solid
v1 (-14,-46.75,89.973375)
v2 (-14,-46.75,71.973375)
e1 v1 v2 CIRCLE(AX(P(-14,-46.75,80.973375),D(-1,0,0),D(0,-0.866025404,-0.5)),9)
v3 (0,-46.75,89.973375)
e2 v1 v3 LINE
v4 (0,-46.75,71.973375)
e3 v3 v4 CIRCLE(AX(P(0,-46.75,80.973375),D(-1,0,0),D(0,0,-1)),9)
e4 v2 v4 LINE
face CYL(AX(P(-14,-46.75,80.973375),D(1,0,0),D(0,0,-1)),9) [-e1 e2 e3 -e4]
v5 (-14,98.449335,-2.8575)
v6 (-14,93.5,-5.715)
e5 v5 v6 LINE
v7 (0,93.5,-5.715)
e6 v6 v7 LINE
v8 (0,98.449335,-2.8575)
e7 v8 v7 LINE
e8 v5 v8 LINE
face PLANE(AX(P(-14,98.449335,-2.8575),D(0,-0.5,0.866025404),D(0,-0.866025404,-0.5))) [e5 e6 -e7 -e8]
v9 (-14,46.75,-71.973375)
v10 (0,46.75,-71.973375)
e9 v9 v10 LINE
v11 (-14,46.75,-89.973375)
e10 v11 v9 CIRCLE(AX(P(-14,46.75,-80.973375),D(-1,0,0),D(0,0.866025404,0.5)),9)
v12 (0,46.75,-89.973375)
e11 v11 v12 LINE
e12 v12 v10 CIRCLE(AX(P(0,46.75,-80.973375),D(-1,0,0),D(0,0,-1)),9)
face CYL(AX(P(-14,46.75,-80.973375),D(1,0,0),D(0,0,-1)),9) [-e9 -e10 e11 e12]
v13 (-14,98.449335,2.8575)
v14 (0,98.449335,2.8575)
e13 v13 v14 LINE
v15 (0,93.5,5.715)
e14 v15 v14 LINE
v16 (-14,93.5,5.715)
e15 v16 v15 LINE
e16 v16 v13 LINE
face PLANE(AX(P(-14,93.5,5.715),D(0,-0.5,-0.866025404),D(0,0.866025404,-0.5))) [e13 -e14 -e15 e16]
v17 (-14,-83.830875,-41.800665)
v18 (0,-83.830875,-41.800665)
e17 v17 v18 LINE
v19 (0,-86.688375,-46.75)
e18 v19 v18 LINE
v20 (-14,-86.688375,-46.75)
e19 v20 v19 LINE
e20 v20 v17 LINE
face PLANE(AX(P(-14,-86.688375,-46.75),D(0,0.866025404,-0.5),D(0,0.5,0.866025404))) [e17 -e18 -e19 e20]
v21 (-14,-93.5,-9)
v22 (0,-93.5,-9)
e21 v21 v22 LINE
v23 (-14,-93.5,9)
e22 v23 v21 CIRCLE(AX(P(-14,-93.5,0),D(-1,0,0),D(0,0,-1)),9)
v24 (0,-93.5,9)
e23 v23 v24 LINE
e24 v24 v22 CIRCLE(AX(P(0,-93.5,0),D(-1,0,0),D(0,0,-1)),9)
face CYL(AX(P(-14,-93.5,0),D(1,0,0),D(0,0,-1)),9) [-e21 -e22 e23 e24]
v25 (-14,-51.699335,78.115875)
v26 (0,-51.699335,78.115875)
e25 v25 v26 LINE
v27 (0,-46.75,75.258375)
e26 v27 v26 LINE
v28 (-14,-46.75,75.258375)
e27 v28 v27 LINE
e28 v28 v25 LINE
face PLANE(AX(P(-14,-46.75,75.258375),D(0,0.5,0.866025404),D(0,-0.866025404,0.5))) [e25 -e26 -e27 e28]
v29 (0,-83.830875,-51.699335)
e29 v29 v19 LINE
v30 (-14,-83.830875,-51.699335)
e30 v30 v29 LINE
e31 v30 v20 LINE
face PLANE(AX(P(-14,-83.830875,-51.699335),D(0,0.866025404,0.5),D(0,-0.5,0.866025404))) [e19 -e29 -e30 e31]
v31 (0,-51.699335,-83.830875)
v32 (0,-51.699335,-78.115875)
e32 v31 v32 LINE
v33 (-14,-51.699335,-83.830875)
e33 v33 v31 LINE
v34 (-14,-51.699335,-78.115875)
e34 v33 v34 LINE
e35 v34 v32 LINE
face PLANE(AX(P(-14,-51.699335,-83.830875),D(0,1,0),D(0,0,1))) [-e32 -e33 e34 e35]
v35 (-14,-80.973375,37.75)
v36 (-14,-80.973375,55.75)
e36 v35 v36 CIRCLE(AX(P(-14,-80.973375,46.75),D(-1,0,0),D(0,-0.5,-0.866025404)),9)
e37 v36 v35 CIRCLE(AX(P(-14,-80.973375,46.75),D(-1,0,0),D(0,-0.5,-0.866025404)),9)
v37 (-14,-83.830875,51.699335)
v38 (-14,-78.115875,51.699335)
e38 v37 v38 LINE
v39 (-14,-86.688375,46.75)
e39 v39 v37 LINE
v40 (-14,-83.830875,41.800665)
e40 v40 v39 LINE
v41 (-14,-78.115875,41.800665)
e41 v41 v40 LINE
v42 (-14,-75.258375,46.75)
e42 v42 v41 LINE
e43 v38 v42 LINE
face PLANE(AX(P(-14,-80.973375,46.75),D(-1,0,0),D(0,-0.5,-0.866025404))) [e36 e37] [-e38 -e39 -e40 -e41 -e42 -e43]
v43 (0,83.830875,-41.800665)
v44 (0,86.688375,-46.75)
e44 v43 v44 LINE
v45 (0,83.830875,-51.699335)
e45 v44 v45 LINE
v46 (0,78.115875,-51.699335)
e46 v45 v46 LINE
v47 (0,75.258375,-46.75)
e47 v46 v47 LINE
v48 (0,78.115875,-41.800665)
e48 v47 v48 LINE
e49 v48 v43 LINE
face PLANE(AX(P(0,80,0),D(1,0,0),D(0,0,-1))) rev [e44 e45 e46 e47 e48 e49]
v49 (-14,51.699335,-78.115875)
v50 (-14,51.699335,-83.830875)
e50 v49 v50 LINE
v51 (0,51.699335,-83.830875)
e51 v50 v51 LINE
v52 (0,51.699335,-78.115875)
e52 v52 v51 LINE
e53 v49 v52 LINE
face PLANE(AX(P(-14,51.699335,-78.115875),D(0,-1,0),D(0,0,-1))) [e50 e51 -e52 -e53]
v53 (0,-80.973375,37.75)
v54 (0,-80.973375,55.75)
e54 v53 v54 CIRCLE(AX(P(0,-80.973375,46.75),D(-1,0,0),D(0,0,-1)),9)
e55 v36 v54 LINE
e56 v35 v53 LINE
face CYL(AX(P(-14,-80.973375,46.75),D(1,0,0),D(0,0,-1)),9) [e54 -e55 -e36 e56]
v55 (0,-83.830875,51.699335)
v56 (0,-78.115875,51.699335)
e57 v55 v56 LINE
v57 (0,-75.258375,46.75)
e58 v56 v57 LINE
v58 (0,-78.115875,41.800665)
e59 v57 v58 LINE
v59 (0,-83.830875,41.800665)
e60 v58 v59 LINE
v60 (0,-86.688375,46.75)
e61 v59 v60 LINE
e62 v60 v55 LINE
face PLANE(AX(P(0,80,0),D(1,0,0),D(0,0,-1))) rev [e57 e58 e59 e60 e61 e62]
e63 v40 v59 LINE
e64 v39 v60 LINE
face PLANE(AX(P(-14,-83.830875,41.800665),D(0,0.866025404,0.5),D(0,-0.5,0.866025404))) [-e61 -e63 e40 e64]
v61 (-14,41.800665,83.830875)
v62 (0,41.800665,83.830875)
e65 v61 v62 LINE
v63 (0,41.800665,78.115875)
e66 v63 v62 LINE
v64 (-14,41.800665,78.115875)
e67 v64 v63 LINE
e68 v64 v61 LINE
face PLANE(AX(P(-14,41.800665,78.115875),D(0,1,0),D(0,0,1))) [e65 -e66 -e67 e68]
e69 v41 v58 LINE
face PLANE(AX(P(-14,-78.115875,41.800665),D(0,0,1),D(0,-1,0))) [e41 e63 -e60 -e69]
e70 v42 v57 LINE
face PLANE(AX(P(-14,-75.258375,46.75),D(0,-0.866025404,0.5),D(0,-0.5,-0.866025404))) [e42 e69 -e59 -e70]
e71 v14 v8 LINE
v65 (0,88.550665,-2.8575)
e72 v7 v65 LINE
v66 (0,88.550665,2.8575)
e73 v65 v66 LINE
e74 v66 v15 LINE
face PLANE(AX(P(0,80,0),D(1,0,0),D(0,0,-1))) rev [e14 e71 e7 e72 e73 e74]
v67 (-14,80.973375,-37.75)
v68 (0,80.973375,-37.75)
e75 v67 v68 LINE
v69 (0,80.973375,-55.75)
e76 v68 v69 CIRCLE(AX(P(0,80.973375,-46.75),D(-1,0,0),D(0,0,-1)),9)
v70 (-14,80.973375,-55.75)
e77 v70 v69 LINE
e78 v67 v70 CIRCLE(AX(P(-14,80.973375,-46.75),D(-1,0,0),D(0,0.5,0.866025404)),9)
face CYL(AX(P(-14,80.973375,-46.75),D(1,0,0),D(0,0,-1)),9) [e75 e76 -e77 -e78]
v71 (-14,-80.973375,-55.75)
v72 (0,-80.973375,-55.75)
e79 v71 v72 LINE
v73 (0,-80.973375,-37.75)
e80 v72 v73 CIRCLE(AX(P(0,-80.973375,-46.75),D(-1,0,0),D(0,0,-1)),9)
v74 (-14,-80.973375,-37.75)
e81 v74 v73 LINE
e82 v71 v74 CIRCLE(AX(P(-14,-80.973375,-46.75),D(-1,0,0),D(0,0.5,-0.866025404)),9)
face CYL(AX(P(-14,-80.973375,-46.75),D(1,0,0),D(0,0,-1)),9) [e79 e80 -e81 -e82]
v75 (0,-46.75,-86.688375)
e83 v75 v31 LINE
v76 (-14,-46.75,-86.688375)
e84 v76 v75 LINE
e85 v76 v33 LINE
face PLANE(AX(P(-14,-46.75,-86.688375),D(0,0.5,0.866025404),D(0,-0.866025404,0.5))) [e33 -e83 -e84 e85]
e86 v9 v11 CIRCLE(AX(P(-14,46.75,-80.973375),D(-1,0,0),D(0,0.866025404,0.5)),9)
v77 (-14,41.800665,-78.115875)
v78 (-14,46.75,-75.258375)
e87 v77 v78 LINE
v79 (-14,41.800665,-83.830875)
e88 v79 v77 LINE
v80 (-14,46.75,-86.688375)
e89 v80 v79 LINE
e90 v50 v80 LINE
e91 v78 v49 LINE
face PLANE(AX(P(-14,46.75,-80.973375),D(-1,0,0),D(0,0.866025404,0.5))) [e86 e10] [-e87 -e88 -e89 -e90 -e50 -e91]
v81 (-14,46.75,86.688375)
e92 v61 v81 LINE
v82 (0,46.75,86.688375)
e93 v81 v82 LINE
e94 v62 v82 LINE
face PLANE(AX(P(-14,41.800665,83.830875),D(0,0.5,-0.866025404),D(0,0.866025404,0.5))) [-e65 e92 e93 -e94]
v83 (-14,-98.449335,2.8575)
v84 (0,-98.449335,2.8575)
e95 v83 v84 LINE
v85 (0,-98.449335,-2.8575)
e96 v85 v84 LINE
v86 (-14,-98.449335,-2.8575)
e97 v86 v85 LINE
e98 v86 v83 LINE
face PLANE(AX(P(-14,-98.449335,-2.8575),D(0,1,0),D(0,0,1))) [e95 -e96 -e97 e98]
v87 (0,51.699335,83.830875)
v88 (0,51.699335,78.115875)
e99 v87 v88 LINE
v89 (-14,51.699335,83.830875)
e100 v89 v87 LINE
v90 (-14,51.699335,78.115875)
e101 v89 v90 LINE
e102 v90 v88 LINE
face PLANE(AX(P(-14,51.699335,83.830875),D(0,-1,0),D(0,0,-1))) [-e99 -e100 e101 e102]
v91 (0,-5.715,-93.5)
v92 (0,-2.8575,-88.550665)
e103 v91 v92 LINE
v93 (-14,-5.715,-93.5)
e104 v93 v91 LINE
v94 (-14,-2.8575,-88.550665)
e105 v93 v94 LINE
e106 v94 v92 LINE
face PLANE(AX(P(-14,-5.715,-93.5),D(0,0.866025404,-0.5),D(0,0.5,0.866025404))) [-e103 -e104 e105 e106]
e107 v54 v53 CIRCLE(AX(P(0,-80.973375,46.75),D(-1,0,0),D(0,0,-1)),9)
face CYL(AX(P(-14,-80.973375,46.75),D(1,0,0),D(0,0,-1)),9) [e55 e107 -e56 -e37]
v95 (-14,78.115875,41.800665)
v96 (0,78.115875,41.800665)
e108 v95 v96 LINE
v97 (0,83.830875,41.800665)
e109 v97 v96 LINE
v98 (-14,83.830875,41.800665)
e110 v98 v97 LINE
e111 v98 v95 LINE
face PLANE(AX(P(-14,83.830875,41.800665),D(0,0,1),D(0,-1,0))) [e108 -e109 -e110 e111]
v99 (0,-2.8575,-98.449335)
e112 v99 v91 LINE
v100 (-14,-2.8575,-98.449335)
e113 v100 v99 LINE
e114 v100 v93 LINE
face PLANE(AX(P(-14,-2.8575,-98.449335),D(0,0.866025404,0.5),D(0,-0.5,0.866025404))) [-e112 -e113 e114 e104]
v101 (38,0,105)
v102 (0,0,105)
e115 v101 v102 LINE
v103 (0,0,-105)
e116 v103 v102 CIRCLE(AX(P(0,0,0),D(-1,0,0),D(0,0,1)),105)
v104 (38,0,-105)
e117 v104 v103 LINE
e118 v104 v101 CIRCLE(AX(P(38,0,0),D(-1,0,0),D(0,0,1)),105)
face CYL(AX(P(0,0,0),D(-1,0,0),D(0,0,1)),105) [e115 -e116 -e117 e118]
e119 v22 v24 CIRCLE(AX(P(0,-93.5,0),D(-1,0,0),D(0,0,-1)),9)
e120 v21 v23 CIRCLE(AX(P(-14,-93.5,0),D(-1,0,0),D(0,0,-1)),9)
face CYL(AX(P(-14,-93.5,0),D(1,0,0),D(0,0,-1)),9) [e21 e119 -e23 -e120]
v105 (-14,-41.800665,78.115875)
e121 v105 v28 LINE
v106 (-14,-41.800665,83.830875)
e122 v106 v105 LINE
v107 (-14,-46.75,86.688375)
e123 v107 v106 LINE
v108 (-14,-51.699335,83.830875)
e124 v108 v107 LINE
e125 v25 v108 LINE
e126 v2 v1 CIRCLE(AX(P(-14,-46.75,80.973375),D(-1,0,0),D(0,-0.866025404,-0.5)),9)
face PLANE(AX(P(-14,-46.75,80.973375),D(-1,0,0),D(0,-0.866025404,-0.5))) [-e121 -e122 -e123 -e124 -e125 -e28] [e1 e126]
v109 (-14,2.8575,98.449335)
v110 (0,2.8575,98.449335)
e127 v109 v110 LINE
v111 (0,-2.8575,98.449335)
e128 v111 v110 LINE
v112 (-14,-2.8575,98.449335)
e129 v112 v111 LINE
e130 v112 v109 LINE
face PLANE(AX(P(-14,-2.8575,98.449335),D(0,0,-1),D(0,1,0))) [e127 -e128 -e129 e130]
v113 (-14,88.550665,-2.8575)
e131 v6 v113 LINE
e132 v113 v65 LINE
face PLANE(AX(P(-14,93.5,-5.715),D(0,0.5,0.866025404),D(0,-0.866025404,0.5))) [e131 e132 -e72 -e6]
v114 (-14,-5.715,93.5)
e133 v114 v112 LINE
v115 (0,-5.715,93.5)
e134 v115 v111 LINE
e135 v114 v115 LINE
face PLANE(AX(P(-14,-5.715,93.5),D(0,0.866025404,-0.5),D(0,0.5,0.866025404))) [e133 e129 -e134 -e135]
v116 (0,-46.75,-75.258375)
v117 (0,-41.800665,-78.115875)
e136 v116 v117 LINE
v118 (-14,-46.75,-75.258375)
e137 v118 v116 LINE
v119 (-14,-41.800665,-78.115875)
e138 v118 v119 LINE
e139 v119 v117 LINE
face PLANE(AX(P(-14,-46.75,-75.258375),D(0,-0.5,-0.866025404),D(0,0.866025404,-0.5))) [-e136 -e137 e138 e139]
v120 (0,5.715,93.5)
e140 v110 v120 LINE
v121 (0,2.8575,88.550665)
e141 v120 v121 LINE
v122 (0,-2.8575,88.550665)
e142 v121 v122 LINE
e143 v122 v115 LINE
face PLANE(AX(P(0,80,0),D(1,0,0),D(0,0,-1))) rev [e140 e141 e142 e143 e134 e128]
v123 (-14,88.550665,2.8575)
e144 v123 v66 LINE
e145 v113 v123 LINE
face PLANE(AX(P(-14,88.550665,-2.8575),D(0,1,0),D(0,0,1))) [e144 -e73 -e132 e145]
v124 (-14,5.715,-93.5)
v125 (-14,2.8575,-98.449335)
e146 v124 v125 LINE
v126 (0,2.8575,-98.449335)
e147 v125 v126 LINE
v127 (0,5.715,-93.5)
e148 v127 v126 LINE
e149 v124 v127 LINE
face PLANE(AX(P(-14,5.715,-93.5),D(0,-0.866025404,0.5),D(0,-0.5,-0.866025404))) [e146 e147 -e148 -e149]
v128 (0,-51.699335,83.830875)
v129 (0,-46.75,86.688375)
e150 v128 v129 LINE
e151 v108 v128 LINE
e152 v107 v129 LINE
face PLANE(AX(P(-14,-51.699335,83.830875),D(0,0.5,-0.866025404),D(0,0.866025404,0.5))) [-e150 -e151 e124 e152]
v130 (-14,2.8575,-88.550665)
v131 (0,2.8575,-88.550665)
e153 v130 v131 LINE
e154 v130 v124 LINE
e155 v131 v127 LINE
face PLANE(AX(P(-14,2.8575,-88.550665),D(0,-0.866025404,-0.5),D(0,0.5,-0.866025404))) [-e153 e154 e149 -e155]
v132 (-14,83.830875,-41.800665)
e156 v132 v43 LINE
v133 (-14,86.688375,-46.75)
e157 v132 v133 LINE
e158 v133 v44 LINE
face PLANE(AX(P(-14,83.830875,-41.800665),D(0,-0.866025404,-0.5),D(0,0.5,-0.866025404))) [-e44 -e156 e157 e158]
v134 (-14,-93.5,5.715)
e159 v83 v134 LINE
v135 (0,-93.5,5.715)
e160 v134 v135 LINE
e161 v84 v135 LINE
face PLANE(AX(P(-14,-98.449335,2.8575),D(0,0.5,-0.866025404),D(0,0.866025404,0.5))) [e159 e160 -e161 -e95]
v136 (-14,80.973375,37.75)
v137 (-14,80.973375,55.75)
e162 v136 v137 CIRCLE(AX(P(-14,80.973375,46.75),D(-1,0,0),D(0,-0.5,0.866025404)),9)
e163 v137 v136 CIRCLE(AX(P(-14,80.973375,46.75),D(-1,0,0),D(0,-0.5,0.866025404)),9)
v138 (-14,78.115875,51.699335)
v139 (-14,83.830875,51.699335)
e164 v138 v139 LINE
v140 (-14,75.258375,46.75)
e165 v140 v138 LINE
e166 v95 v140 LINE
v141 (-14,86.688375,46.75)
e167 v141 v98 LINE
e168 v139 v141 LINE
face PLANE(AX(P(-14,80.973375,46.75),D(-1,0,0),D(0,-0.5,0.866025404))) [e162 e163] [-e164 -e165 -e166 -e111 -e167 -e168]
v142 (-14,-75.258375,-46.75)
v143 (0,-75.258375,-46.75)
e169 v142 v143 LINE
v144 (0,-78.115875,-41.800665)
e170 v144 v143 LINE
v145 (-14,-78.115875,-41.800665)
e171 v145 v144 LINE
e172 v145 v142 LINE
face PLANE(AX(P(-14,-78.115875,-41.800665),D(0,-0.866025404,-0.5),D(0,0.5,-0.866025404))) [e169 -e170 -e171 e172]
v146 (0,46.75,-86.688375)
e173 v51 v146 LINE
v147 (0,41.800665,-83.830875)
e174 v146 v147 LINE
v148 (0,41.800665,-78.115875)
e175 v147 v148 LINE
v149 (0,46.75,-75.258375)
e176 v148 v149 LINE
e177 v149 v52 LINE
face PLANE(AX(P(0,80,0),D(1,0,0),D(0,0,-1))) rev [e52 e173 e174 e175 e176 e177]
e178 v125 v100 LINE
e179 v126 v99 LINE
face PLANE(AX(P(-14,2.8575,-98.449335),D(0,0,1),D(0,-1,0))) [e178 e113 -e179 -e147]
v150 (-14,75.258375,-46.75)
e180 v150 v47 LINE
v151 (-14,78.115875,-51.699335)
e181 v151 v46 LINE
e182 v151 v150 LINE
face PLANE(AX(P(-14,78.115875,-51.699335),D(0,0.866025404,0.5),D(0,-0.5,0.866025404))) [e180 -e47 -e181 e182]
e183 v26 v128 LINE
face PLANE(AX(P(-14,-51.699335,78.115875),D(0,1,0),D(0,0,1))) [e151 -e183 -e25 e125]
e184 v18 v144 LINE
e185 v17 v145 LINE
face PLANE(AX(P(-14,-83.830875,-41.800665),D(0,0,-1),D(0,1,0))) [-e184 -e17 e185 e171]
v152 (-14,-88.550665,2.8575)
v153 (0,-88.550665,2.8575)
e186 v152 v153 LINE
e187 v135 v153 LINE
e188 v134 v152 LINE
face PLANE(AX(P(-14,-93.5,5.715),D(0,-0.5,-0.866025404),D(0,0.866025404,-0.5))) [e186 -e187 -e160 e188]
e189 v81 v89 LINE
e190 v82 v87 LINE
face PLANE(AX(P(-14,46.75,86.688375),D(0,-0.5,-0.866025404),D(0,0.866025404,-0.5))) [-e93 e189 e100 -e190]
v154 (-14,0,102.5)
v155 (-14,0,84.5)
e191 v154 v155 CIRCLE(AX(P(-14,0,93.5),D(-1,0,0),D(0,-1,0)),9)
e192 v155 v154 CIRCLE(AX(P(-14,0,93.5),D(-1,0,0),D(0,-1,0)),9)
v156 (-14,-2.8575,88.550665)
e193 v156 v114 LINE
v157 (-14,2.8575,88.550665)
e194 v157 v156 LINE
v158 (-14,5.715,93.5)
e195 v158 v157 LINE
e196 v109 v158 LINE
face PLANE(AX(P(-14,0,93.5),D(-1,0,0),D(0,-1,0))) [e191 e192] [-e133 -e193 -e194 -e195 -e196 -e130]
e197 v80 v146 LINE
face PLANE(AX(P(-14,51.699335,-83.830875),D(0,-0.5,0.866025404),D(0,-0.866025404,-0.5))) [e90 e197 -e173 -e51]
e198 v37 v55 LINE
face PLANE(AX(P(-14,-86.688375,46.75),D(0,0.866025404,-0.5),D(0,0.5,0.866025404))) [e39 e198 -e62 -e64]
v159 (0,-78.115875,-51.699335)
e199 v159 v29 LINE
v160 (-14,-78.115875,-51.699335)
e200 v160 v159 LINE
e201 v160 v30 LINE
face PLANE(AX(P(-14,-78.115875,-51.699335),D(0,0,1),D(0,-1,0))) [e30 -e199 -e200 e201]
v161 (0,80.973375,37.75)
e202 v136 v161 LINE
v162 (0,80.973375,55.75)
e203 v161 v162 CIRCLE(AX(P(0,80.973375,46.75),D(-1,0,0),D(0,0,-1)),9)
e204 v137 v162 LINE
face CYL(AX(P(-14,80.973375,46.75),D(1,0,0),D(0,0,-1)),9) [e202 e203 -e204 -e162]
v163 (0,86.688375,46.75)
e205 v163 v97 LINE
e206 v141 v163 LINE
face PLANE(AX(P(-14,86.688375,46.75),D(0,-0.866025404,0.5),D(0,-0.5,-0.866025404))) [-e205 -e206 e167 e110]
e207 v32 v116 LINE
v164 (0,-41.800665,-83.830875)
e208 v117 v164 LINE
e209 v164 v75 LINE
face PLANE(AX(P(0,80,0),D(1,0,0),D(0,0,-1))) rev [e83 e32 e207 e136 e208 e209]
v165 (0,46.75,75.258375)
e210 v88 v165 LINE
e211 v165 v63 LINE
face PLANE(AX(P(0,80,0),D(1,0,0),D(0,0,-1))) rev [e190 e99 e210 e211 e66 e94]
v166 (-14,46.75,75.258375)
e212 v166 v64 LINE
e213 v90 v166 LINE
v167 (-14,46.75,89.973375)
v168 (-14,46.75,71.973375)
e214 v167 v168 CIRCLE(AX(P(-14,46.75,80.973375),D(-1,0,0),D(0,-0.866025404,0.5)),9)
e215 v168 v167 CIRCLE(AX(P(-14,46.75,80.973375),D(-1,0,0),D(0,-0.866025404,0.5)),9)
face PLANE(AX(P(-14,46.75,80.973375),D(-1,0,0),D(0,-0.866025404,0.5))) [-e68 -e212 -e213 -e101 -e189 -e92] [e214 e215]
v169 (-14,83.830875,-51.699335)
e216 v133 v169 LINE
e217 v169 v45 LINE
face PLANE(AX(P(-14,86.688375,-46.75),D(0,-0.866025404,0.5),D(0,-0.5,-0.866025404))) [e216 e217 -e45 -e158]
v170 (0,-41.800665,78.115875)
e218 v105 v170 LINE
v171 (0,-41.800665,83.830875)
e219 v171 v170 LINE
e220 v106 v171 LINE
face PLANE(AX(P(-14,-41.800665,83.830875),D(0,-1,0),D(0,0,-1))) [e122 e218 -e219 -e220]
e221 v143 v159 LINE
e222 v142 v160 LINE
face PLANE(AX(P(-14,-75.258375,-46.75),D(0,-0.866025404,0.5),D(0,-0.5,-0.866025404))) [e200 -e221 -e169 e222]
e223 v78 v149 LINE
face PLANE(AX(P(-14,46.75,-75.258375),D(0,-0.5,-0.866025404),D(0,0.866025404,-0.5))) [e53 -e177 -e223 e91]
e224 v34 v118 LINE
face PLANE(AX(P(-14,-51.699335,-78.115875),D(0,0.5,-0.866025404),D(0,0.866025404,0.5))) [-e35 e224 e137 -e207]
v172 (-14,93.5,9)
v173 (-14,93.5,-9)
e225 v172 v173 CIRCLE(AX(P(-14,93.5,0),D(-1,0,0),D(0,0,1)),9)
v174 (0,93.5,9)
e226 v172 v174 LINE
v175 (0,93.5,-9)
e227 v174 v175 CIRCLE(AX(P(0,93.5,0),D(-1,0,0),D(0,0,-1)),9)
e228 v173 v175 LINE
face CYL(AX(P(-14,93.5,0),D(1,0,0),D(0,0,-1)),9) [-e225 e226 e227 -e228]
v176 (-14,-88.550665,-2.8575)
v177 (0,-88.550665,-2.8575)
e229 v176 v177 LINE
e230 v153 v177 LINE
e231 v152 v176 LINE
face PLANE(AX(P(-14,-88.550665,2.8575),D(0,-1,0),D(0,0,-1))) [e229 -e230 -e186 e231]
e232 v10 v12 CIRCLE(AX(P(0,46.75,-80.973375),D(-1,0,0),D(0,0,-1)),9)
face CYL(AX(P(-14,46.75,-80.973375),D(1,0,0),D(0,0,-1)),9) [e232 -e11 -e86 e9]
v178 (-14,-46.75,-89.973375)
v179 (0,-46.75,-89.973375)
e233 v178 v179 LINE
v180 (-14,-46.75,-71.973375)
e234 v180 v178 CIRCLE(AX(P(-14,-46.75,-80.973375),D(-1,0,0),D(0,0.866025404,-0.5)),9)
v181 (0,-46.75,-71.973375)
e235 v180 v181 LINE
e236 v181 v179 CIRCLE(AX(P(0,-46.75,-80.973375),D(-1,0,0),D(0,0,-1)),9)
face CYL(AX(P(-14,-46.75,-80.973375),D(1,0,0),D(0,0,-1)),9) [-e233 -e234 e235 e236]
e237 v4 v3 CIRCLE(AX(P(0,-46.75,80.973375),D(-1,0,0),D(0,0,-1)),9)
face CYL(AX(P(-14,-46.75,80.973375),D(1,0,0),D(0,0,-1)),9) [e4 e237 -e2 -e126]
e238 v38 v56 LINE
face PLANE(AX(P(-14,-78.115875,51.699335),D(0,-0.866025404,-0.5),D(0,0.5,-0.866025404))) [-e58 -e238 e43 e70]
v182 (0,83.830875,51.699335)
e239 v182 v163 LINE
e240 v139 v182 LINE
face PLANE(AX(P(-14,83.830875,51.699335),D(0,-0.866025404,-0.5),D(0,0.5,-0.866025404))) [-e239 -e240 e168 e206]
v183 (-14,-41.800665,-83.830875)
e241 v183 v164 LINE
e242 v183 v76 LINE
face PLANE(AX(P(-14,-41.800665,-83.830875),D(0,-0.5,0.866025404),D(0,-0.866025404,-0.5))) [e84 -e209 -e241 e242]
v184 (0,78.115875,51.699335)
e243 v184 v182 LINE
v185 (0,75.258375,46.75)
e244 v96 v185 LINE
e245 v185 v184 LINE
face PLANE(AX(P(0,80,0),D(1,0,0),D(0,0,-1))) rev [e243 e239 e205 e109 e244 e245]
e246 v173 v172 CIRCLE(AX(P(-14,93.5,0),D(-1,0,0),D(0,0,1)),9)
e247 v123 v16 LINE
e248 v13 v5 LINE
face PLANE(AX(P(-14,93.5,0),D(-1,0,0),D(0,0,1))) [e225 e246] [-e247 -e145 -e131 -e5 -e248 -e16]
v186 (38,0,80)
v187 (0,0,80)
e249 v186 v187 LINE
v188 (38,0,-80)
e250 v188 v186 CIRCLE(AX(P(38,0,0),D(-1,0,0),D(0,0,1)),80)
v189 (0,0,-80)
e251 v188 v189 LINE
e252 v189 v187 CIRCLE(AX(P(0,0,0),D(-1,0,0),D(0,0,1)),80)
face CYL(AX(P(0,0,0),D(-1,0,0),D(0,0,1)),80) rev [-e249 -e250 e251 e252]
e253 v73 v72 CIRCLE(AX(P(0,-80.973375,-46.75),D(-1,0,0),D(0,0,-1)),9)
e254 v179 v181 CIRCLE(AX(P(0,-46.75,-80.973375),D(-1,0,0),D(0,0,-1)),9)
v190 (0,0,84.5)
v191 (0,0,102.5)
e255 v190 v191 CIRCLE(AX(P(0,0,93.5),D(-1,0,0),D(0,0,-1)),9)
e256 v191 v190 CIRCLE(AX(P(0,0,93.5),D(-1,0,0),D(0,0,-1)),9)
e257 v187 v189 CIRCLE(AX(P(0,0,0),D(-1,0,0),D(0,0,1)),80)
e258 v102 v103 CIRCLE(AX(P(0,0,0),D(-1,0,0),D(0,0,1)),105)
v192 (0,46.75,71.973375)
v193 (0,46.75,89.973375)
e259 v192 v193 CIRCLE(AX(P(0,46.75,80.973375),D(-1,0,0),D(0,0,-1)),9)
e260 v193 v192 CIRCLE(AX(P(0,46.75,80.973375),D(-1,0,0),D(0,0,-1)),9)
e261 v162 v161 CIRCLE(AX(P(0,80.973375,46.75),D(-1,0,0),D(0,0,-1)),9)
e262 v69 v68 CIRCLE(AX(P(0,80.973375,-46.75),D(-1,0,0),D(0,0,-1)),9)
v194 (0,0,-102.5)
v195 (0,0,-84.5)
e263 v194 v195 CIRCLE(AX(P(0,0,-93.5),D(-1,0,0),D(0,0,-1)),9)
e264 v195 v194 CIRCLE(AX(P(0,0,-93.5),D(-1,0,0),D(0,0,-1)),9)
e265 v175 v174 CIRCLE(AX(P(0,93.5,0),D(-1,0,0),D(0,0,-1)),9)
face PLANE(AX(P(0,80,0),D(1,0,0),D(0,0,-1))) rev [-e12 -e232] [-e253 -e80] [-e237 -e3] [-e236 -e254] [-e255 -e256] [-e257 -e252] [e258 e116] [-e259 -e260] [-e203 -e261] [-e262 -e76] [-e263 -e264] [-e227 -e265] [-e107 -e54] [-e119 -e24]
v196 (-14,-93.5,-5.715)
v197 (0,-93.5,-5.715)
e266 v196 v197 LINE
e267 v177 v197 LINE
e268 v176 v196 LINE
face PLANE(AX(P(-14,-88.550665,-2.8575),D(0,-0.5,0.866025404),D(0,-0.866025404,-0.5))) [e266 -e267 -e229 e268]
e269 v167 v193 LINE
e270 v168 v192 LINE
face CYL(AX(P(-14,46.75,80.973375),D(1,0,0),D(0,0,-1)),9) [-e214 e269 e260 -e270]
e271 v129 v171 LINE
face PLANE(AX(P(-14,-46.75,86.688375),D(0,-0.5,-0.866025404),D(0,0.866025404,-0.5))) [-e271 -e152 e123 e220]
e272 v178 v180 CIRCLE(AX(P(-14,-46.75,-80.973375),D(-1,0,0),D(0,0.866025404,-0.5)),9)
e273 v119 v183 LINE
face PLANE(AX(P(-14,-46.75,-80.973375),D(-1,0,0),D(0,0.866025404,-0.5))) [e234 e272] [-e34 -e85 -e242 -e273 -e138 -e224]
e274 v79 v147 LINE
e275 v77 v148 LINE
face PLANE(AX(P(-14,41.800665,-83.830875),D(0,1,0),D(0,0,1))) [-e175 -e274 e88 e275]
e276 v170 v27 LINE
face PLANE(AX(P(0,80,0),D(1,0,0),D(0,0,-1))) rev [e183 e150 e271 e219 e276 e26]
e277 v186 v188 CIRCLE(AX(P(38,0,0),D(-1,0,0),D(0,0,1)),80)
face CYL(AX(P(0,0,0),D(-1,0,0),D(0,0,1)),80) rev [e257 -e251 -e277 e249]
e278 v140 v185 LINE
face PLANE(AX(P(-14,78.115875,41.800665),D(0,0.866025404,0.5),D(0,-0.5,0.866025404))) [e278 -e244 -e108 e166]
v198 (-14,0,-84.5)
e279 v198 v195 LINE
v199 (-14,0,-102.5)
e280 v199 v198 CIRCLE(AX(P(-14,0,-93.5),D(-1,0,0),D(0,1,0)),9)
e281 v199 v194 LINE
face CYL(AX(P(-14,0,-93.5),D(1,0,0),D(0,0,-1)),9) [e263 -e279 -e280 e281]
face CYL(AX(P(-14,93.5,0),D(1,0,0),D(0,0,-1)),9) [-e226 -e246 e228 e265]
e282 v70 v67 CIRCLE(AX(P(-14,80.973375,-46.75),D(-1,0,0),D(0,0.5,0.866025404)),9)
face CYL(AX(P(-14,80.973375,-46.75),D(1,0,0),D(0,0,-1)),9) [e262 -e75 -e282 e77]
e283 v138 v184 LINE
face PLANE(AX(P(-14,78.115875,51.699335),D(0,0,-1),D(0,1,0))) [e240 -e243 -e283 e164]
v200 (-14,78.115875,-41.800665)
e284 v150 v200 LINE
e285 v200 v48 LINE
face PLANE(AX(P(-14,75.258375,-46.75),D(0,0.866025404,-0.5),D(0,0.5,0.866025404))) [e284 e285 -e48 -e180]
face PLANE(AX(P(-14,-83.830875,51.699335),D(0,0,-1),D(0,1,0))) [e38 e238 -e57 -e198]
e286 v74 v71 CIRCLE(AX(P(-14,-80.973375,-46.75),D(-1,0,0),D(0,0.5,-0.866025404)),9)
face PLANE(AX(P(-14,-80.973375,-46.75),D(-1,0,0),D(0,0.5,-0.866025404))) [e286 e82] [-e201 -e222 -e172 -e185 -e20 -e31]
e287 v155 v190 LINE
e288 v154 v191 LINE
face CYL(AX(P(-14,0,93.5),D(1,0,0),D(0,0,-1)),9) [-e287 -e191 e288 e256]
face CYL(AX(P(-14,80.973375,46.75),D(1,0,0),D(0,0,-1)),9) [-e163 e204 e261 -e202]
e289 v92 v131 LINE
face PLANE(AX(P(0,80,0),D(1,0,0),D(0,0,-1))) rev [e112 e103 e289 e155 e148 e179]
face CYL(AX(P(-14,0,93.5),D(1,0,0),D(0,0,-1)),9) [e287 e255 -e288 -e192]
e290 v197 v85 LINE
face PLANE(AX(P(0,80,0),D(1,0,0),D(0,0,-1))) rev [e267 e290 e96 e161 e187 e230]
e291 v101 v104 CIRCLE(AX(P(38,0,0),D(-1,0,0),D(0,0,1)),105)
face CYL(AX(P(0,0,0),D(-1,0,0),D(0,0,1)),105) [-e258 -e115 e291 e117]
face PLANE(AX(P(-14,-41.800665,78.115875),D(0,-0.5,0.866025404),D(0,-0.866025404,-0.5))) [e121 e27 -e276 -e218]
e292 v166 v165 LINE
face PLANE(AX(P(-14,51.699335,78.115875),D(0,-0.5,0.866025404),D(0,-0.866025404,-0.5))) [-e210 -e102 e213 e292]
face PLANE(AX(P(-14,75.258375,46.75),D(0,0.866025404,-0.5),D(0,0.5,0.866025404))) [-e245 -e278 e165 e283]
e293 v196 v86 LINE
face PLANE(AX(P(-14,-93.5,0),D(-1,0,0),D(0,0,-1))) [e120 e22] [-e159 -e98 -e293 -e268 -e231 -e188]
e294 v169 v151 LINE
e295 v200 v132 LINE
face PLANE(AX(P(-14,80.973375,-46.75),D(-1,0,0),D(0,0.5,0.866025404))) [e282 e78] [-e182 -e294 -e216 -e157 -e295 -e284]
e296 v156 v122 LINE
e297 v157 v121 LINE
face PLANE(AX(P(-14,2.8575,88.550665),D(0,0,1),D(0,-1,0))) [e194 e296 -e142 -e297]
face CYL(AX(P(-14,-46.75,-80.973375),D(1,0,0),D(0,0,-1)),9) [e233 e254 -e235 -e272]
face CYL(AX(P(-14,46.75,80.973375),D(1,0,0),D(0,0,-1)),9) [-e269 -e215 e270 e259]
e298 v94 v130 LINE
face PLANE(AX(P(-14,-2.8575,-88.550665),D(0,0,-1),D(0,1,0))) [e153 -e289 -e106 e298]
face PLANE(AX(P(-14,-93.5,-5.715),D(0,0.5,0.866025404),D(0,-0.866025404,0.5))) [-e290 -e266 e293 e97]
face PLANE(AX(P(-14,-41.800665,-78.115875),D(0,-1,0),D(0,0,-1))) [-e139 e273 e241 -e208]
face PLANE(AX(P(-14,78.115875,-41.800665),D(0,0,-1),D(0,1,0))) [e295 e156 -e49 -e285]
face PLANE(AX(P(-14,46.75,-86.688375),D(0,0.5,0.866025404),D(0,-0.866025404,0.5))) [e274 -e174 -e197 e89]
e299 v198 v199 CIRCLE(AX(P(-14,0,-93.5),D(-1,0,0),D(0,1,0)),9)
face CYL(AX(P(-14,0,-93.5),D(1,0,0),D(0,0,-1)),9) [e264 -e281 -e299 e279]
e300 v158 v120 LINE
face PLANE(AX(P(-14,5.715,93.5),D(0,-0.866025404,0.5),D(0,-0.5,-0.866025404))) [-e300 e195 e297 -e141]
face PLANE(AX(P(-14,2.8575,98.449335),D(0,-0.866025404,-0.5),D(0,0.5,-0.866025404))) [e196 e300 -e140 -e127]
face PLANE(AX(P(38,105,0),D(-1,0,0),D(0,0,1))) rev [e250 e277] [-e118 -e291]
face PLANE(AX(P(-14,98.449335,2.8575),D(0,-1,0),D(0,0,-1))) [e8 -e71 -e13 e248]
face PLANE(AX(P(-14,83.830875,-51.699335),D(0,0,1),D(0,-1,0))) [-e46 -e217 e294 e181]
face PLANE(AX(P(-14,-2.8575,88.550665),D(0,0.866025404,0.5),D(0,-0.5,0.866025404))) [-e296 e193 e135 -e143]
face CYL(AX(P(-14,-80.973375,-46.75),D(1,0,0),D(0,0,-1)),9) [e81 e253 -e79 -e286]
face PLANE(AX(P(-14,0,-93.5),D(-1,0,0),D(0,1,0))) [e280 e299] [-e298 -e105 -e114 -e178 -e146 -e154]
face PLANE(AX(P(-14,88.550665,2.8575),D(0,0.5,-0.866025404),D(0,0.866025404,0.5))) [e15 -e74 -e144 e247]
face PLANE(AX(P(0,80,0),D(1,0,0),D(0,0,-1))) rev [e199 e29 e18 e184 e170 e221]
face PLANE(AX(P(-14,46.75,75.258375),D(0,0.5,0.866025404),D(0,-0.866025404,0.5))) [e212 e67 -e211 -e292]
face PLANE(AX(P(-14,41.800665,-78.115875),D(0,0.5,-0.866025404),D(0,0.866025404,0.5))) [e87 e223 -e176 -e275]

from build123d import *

# Parameters (mm, degrees)
SKETCH1_W           = 38
SKETCH1_H           = 25
SKETCH2_R           = 9
BOSS_EXTRUDE1_DEPTH = 14
CIRPATTERN1_COUNT   = 12


with BuildPart() as part:
    # Sketch1 → Revolve1 (revolve)
    with BuildSketch(Plane.XY, mode=Mode.PRIVATE) as revolve1_sk:
        with Locations((19, 92.5)):
            Rectangle(SKETCH1_W, SKETCH1_H)
    revolve(revolve1_sk.sketch.rotate(Axis((0, 0, 0), (1, 0, 0)), 90), axis=Axis((0, 0, 0), (1, 0, 0)))

    # Sketch2 → Boss-Extrude1 (add)
    with BuildSketch(Plane.ZY):
        with Locations(Location((0, 93.5, 0), (0, 0, 180))):
            Circle(SKETCH2_R)
        Polygon((5.715, 93.5), (2.8575, 98.449335183), (-2.8575, 98.449335183), (-5.715, 93.5), (-2.8575, 88.550664817), (2.8575, 88.550664817), align=None, mode=Mode.SUBTRACT)
    boss_extrude1 = extrude(amount=BOSS_EXTRUDE1_DEPTH)

    # CirPattern1: Boss-Extrude1 ×12 about axis
    cirpattern1_axis = Axis((0, 0, 0), (1, 0, 0))
    for i in range(1, CIRPATTERN1_COUNT):
        add(boss_extrude1.rotate(cirpattern1_axis, i * 360 / CIRPATTERN1_COUNT))


solid = part.part
